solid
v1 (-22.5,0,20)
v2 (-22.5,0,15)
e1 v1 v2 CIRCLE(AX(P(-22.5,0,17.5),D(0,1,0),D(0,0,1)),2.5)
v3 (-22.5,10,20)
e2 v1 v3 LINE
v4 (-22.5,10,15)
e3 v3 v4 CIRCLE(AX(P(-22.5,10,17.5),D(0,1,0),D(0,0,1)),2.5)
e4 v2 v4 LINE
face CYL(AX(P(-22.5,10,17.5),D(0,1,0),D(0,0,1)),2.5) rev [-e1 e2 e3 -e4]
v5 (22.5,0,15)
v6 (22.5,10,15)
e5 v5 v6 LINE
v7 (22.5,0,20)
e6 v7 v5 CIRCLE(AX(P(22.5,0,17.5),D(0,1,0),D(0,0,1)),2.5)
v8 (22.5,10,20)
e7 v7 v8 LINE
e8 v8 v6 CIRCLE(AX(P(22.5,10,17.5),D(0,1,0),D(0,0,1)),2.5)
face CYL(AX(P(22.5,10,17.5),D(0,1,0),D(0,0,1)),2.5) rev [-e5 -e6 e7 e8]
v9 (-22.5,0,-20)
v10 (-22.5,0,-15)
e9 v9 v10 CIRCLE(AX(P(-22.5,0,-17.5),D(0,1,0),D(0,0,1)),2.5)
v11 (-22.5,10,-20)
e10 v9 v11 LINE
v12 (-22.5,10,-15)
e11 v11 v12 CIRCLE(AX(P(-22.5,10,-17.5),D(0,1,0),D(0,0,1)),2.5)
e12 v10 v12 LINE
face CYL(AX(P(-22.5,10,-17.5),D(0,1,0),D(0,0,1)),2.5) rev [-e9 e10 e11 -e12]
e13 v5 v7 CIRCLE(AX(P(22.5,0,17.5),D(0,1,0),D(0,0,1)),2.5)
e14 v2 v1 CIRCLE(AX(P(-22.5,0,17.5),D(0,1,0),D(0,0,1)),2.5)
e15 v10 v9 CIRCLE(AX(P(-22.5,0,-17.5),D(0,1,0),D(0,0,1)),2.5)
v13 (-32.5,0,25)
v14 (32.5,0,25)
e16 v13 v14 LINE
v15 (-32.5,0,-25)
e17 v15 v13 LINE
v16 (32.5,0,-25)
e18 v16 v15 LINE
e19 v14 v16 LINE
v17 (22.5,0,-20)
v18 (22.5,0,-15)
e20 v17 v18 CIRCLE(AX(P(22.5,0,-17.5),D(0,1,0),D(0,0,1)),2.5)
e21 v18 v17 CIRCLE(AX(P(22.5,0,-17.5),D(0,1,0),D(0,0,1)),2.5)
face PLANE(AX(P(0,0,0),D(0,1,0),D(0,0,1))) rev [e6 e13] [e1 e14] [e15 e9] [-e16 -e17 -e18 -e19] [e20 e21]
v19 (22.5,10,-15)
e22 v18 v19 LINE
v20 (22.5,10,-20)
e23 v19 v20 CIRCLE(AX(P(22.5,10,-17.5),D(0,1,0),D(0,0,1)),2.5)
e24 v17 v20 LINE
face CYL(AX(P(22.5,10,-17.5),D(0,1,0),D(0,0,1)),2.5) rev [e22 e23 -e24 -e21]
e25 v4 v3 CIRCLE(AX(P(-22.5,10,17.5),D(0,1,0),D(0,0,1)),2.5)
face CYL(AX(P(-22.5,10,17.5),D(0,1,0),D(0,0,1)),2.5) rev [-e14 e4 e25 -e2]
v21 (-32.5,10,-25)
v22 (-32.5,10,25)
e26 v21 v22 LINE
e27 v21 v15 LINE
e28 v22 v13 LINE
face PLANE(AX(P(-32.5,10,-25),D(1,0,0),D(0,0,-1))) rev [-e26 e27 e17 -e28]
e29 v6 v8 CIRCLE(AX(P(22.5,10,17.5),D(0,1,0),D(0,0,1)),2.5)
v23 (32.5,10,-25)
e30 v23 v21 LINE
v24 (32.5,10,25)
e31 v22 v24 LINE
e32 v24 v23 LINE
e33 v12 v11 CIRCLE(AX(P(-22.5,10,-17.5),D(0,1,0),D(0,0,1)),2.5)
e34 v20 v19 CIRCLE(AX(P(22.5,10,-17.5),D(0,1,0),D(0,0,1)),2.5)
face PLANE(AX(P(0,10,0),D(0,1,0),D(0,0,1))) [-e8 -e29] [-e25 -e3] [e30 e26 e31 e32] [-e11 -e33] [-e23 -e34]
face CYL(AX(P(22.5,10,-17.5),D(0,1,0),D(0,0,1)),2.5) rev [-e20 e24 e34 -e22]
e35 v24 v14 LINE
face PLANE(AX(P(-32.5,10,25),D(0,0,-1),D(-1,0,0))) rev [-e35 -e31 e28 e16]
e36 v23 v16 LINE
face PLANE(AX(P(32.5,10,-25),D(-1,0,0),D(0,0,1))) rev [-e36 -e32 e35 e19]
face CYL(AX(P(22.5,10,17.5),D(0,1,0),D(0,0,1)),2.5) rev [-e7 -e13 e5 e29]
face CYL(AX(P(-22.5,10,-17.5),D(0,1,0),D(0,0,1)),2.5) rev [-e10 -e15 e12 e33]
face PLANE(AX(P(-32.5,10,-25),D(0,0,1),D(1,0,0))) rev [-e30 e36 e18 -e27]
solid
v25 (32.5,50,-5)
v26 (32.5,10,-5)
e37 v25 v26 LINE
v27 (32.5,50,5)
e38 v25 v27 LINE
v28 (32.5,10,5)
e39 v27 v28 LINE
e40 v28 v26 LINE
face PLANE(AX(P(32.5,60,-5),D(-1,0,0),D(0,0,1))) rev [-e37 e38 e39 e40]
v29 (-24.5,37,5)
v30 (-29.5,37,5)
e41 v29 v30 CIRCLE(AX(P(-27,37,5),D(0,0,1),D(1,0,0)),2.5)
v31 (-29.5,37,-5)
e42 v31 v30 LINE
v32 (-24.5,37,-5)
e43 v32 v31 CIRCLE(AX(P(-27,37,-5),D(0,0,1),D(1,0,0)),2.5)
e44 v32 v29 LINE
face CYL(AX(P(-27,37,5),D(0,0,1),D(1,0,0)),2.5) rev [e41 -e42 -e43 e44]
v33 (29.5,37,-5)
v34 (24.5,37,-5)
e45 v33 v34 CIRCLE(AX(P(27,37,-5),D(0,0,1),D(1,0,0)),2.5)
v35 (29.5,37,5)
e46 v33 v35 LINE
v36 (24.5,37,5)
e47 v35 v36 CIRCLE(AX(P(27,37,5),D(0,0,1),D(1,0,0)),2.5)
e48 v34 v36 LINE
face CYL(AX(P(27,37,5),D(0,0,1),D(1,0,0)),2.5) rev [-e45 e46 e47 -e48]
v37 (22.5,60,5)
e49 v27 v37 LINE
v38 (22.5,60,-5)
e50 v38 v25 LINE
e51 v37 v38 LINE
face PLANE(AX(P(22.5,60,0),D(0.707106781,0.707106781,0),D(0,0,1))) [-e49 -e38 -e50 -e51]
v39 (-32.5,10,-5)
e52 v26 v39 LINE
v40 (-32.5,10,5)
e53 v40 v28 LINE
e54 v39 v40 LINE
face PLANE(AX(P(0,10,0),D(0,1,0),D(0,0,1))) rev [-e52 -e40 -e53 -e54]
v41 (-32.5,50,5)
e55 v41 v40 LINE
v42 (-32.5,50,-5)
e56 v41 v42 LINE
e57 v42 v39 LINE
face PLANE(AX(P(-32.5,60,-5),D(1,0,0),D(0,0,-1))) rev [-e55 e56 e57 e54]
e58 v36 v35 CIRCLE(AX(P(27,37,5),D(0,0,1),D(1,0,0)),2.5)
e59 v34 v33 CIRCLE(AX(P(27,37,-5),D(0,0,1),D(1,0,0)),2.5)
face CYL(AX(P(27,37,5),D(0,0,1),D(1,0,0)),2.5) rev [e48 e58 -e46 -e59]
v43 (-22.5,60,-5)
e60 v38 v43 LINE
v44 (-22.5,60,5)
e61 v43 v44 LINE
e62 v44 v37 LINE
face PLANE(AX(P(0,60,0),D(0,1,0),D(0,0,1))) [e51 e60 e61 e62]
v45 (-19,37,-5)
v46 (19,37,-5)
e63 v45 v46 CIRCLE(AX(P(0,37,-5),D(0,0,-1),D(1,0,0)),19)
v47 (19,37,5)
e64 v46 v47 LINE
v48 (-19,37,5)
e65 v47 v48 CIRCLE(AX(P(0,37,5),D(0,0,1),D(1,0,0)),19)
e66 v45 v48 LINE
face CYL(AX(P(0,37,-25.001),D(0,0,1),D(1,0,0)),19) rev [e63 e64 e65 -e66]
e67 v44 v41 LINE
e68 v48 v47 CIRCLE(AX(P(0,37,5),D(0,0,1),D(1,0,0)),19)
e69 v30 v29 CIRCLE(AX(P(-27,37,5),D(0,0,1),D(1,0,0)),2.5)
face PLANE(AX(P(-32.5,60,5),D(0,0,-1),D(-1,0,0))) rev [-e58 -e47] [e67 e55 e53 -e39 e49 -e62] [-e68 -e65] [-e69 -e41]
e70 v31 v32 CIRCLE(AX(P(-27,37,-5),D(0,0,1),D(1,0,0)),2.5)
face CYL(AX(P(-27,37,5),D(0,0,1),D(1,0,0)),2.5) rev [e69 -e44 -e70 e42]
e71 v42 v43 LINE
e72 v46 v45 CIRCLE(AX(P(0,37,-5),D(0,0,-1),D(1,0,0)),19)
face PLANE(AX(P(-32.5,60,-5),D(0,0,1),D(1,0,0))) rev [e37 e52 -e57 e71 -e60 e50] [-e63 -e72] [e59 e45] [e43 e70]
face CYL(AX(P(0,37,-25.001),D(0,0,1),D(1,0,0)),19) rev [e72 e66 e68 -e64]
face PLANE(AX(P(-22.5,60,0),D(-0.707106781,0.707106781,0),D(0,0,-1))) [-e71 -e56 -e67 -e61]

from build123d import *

# Parameters (mm, degrees)
SKETCH1_W                  = 65
SKETCH1_H                  = 50
BOSS_EXTRUDE1_DEPTH        = 10
SKETCH2_W                  = 65
SKETCH2_H                  = 10
BOSS_EXTRUDE2_DEPTH        = 50
SKETCH3_R                  = 19
CUT_EXTRUDE1_DEPTH         = 10
CHAMFER1_SIZE              = 10
SKETCH5_W                  = 2.5
SKETCH5_H                  = 10
M6_TAPPED_HOLE2_AT_2_COUNT = 2
M6_TAPPED_HOLE2_AT_2_PITCH = 57.008771255
M6_TAPPED_HOLE2_AT_3_COUNT = 2
M6_TAPPED_HOLE2_AT_3_PITCH = 45
M6_TAPPED_HOLE2_AT_4_COUNT = 2
M6_TAPPED_HOLE2_AT_4_PITCH = 35
SKETCH7_W                  = 2.5
SKETCH7_H                  = 10
M6_TAPPED_HOLE1_AT_2_COUNT = 2
M6_TAPPED_HOLE1_AT_2_PITCH = 54


with BuildPart() as part:
    # Sketch1 → Boss-Extrude1 (new body)
    with BuildSketch(Plane(origin=(0, 0, 0), x_dir=(1, 0, 0), z_dir=(0, 1, 0))):
        Rectangle(SKETCH1_W, SKETCH1_H)
    extrude(amount=BOSS_EXTRUDE1_DEPTH)

    # Sketch5 → M6 Tapped Hole2 (revolve, cut)
    with BuildSketch(Plane(origin=(22.5, 10, 17.5), x_dir=(0, 0, 1), z_dir=(1, 0, 0))):
        with Locations((1.25, 5)):
            Rectangle(SKETCH5_W, SKETCH5_H)
    m6_tapped_hole2 = revolve(axis=Axis((22.5, 16.35, 17.5), (0, -1, 0)), mode=Mode.SUBTRACT)

    # M6 Tapped Hole2 at 2: M6 Tapped Hole2 ×2
    with Locations(*[Vector(-0.7893522173763263, 0, -0.6139406135149205) * (i * M6_TAPPED_HOLE2_AT_2_PITCH) for i in range(1, M6_TAPPED_HOLE2_AT_2_COUNT)]):
        add(m6_tapped_hole2, mode=Mode.SUBTRACT)

    # M6 Tapped Hole2 at 3: M6 Tapped Hole2 ×2
    with Locations(*[(-i * M6_TAPPED_HOLE2_AT_3_PITCH, 0, 0) for i in range(1, M6_TAPPED_HOLE2_AT_3_COUNT)]):
        add(m6_tapped_hole2, mode=Mode.SUBTRACT)

    # M6 Tapped Hole2 at 4: M6 Tapped Hole2 ×2
    with Locations(*[(0, 0, -i * M6_TAPPED_HOLE2_AT_4_PITCH) for i in range(1, M6_TAPPED_HOLE2_AT_4_COUNT)]):
        add(m6_tapped_hole2, mode=Mode.SUBTRACT)


with BuildPart() as body_2:
    # Sketch2 → Boss-Extrude2 (new body)
    with BuildSketch(Plane(origin=(0, 10, 0), x_dir=(1, 0, 0), z_dir=(0, 1, 0))):
        Rectangle(SKETCH2_W, SKETCH2_H)
    extrude(amount=BOSS_EXTRUDE2_DEPTH)

    # Sketch3 → Cut-Extrude1 (cut)
    with BuildSketch(Plane.XY.offset(5)):
        with Locations((0, 37)):
            Circle(SKETCH3_R)
    extrude(amount=-CUT_EXTRUDE1_DEPTH, mode=Mode.SUBTRACT)

    # Chamfer1
    chamfer1_edges = [body_2.edges().sort_by_distance(p)[0] for p in [
        (-32.5, 60, 0),
        (32.5, 60, 0),
    ]]
    chamfer(chamfer1_edges, length=CHAMFER1_SIZE)

    # Sketch7 → M6 Tapped Hole1 (revolve, cut)
    with BuildSketch(Plane(origin=(-27, 37, 5), x_dir=(0, -1, 0), z_dir=(1, 0, 0))):
        with Locations((1.25, 5)):
            Rectangle(SKETCH7_W, SKETCH7_H)
    m6_tapped_hole1 = revolve(axis=Axis((-27, 37, 11.35), (0, 0, -1)), mode=Mode.SUBTRACT)

    # M6 Tapped Hole1 at 2: M6 Tapped Hole1 ×2
    with Locations(*[(i * M6_TAPPED_HOLE1_AT_2_PITCH, 0, 0) for i in range(1, M6_TAPPED_HOLE1_AT_2_COUNT)]):
        add(m6_tapped_hole1, mode=Mode.SUBTRACT)


solid = Compound([part.part, body_2.part])
